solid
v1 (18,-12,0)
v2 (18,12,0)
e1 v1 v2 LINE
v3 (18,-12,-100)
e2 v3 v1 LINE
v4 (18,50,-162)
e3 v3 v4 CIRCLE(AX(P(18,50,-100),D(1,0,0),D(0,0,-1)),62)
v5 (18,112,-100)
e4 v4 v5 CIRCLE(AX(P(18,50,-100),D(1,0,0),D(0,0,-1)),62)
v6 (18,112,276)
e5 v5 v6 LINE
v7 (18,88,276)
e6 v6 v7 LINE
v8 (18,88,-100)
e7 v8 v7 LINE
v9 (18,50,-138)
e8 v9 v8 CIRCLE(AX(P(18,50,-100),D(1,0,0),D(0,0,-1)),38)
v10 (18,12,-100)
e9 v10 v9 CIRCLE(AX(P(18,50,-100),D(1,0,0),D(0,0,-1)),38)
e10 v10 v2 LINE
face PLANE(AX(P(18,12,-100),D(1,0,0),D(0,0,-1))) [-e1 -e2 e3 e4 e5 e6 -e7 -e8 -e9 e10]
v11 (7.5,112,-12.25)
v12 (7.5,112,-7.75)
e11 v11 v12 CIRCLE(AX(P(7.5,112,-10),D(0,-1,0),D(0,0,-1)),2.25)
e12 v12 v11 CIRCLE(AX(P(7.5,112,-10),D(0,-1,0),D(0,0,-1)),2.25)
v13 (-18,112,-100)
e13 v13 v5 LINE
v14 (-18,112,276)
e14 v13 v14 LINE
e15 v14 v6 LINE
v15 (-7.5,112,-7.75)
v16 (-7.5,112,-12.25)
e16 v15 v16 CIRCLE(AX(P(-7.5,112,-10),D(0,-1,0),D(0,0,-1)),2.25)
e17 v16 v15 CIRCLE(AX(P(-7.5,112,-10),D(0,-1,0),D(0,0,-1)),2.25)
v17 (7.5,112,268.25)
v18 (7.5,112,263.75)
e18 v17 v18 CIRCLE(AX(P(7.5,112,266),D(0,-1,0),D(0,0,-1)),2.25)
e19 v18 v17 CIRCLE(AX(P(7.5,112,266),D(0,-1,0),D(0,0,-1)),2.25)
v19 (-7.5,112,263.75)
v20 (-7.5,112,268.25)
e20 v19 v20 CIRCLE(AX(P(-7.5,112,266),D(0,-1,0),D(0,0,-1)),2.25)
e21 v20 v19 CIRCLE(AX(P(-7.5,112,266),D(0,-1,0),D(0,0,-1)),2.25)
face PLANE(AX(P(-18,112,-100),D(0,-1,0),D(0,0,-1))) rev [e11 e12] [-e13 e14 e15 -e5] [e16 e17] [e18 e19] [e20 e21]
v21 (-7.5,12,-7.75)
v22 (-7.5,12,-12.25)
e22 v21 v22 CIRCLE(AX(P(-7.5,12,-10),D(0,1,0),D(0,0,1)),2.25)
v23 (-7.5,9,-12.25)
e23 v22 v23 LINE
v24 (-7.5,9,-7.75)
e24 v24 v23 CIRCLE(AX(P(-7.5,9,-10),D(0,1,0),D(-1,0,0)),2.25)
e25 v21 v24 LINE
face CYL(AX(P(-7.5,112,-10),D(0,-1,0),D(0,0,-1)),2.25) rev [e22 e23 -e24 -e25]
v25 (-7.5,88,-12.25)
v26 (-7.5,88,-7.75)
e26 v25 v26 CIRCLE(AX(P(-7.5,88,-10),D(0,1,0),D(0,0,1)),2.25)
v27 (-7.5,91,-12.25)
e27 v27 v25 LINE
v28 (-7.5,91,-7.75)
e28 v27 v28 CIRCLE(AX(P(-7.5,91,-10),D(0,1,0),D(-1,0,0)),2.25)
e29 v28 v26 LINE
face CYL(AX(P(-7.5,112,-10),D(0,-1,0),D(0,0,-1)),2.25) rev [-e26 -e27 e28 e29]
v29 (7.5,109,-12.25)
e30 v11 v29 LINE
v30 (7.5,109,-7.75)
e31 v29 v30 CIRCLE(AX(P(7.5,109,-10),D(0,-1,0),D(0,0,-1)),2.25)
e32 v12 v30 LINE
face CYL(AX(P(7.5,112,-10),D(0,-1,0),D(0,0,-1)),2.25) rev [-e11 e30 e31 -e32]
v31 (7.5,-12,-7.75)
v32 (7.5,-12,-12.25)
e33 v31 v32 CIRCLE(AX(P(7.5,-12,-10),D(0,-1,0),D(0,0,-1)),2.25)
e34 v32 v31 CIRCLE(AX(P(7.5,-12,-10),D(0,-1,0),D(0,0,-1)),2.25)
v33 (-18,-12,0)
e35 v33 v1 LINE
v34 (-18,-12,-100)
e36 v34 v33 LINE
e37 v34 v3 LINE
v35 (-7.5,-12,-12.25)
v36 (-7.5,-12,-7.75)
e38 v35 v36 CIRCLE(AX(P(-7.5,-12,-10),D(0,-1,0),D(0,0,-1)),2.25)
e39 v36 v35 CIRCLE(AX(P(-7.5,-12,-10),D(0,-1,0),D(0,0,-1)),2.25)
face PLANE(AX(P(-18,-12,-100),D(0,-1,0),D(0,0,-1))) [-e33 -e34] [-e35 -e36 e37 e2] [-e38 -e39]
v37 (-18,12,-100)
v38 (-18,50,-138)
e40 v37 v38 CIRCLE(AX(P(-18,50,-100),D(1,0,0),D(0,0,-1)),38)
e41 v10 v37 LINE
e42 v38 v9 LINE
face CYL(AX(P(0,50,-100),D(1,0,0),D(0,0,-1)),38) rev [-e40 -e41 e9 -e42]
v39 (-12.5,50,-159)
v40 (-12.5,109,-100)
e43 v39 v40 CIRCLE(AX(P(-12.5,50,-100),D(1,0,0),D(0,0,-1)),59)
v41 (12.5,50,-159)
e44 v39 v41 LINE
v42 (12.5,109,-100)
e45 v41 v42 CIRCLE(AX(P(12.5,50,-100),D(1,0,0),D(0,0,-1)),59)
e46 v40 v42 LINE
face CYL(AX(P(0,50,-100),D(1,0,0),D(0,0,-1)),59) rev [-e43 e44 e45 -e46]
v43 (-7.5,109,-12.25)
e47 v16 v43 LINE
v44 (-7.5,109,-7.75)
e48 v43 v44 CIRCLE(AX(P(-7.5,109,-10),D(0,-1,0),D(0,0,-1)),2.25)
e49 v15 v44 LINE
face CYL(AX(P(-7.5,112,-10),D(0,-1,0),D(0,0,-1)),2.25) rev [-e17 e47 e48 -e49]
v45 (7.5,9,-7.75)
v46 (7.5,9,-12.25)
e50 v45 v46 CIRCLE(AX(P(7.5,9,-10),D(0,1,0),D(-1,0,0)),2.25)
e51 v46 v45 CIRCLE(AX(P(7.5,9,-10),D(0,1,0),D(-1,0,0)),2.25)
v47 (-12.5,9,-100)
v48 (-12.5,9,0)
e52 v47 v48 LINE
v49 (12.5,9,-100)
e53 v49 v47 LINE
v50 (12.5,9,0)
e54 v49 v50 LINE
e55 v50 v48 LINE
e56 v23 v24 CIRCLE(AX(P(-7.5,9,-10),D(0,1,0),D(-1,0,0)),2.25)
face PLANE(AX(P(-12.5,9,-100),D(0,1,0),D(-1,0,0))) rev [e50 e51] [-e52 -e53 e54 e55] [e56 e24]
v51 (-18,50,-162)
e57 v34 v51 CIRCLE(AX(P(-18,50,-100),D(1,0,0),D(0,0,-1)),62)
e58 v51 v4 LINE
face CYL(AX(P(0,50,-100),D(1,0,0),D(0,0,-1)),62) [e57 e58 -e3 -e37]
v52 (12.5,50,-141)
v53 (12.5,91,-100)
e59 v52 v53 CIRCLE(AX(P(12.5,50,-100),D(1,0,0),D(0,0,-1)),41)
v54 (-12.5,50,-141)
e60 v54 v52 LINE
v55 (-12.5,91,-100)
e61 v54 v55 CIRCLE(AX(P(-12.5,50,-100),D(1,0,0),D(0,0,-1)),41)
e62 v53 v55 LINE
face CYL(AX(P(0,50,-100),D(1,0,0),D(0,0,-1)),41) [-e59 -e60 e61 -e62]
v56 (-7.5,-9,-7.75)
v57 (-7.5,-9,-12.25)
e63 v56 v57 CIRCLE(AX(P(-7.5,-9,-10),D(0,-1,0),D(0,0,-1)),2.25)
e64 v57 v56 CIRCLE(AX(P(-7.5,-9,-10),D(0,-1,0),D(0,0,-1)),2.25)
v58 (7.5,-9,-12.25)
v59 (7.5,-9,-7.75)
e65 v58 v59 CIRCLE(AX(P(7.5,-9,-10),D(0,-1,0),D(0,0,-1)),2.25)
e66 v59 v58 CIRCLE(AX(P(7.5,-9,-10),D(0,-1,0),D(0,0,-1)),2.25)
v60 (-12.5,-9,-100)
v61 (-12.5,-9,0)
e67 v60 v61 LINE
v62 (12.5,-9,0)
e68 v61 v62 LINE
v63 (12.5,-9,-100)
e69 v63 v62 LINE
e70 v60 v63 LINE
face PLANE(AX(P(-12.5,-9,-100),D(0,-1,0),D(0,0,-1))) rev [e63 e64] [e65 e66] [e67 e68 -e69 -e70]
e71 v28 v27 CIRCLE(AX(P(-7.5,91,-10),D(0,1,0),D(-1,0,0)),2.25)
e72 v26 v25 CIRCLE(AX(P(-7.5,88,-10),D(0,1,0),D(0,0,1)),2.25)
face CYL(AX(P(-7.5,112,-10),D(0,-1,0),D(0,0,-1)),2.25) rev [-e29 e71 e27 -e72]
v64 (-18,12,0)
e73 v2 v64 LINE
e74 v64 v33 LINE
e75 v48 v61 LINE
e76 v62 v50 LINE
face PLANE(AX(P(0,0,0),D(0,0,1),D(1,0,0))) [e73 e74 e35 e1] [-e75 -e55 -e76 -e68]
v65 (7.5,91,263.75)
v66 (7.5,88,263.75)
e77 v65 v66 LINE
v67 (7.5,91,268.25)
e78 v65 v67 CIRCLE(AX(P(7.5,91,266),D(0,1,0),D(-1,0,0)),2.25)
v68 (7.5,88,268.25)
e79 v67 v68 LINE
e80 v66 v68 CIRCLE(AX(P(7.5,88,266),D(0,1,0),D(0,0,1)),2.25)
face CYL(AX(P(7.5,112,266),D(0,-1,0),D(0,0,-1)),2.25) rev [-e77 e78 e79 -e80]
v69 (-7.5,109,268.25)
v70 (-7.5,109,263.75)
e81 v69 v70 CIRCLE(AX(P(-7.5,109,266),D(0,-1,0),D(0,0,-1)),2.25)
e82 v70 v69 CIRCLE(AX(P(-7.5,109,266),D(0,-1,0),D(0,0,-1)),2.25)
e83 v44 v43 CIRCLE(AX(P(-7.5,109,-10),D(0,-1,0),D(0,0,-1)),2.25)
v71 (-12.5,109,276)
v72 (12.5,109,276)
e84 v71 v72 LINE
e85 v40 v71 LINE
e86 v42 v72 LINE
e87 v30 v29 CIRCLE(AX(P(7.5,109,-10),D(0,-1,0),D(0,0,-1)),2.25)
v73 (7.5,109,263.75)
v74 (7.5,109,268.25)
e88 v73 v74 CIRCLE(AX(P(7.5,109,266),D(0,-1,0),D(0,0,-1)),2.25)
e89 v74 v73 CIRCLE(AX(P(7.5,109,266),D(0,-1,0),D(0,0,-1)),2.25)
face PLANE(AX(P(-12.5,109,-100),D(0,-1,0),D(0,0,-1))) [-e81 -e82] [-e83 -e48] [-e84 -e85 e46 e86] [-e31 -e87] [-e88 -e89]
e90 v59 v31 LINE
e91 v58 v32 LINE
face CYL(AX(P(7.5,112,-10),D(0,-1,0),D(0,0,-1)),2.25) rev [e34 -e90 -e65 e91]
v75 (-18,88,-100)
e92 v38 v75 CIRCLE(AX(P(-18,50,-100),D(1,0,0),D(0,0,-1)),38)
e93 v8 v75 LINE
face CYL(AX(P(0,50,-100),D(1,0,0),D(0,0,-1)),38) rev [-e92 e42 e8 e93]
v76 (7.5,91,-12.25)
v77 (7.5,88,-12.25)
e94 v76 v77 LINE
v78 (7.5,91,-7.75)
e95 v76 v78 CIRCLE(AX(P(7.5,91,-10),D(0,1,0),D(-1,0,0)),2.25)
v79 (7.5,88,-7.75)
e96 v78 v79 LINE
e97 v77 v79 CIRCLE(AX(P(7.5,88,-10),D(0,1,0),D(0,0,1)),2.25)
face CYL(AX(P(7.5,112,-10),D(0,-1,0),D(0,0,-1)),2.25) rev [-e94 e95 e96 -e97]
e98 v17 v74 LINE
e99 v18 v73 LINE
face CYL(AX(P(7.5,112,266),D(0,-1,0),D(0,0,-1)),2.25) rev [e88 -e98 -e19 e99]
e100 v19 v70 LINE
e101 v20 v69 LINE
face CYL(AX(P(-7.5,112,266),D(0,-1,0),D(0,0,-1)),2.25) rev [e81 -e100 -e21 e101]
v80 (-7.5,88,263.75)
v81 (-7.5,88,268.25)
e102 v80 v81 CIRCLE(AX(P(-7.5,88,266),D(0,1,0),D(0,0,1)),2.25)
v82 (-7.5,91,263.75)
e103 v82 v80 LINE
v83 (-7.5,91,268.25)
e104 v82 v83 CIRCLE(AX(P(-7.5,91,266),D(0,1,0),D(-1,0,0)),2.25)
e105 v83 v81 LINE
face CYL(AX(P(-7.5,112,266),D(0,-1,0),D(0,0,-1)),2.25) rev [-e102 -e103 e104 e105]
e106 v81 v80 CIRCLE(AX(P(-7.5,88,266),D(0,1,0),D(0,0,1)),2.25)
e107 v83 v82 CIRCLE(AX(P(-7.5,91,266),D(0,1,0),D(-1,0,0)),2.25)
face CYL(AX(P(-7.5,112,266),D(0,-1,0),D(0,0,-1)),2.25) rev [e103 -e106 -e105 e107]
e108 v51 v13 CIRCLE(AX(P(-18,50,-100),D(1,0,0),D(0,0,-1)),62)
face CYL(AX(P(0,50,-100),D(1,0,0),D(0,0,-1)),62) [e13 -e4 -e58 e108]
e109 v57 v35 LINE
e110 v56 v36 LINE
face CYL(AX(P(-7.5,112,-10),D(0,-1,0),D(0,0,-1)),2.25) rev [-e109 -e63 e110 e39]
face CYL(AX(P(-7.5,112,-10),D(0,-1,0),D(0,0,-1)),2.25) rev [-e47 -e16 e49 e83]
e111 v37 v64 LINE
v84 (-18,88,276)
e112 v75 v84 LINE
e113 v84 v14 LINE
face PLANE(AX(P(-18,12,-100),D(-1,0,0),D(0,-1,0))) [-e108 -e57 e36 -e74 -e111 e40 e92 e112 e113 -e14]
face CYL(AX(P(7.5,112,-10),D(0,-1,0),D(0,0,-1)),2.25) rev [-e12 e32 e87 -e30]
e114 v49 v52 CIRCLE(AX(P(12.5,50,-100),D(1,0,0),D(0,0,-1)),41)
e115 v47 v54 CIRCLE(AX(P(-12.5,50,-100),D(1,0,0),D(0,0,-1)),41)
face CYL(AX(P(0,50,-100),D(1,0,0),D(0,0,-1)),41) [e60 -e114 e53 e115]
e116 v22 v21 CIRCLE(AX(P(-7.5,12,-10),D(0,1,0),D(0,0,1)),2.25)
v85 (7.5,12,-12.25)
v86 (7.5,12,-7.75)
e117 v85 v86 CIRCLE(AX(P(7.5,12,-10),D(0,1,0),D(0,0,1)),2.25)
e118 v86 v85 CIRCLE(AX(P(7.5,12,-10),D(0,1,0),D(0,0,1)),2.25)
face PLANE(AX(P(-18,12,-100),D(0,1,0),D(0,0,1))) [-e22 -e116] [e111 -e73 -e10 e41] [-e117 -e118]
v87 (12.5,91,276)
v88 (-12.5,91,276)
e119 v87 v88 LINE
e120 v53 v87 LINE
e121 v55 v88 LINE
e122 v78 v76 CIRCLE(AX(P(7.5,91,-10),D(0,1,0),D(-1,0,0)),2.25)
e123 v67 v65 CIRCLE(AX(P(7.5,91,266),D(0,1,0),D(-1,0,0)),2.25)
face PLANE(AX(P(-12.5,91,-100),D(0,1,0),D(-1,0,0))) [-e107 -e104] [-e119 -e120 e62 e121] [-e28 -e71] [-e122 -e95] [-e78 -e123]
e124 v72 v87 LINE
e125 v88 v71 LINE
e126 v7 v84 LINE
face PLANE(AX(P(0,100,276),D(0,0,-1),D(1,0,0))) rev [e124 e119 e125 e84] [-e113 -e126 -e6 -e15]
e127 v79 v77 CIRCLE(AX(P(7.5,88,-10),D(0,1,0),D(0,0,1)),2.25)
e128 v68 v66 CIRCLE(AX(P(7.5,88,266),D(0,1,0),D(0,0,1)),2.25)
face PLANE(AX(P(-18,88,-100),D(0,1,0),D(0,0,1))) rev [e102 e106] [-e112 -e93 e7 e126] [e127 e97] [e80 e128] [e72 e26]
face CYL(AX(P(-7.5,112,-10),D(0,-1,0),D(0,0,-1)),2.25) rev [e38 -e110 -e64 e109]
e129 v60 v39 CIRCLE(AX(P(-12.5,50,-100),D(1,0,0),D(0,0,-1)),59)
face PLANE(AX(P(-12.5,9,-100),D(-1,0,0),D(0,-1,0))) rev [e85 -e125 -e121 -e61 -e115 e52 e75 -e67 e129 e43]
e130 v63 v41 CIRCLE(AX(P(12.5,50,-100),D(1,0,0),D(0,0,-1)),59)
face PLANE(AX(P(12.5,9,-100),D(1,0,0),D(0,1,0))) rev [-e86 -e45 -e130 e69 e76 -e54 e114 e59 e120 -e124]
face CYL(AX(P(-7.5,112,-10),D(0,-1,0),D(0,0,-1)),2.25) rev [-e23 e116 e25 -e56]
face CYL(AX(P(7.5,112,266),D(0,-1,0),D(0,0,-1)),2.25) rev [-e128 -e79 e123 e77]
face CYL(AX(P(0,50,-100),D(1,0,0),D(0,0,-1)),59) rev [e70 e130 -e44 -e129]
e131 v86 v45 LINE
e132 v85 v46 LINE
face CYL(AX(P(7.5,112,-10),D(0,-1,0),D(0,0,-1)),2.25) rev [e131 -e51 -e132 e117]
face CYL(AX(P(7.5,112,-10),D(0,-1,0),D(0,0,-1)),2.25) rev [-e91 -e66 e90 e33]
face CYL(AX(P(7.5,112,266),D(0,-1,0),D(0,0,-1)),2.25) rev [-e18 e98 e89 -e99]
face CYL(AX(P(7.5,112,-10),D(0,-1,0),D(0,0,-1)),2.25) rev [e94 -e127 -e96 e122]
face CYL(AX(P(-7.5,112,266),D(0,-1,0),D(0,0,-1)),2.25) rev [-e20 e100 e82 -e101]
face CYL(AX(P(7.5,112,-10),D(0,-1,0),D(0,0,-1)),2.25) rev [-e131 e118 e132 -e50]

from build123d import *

# Parameters (mm, degrees)
SKETCH_2_W          = 36
SKETCH_2_H          = 24
SKETCH_2_W_2        = 25
SKETCH_2_H_2        = 18
SKETCH_4_R          = 2.25
CUT_EXTRUDE_1_DEPTH = 304.110540892


with BuildPart() as part:
    # 扫描1: sweep along a path in 草图3
    with BuildLine(Plane(origin=(0, 0, 0), x_dir=(0, 0, -1), z_dir=(1, 0, 0))) as sweep_1_path:
        Line((0, 0), (100, 0))
        ThreePointArc((100, 0), (150, 50), (100, 100))
        Line((100, 100), (-276, 100))
    # 草图2 → 扫描1 (sweep)
    with BuildSketch(Plane.XY):
        Rectangle(SKETCH_2_W, SKETCH_2_H)
        Rectangle(SKETCH_2_W_2, SKETCH_2_H_2, mode=Mode.SUBTRACT)
    sweep(path=sweep_1_path.line)

    # 草图4 → 切除-拉伸1 (cut, through all)
    with BuildSketch(Plane.XZ.offset(12)):
        with Locations(Location((-7.5, -10, 0), (0, 0, 180))):
            Circle(SKETCH_4_R)
        with Locations(Location((7.5, -10, 0), (0, 0, 180))):
            Circle(SKETCH_4_R)
        with Locations(Location((-7.5, 266, 0), (0, 0, 270))):
            Circle(SKETCH_4_R)
        with Locations(Location((7.5, 266, 0), (0, 0, 270))):
            Circle(SKETCH_4_R)
    extrude(amount=-CUT_EXTRUDE_1_DEPTH, mode=Mode.SUBTRACT)


solid = part.part
